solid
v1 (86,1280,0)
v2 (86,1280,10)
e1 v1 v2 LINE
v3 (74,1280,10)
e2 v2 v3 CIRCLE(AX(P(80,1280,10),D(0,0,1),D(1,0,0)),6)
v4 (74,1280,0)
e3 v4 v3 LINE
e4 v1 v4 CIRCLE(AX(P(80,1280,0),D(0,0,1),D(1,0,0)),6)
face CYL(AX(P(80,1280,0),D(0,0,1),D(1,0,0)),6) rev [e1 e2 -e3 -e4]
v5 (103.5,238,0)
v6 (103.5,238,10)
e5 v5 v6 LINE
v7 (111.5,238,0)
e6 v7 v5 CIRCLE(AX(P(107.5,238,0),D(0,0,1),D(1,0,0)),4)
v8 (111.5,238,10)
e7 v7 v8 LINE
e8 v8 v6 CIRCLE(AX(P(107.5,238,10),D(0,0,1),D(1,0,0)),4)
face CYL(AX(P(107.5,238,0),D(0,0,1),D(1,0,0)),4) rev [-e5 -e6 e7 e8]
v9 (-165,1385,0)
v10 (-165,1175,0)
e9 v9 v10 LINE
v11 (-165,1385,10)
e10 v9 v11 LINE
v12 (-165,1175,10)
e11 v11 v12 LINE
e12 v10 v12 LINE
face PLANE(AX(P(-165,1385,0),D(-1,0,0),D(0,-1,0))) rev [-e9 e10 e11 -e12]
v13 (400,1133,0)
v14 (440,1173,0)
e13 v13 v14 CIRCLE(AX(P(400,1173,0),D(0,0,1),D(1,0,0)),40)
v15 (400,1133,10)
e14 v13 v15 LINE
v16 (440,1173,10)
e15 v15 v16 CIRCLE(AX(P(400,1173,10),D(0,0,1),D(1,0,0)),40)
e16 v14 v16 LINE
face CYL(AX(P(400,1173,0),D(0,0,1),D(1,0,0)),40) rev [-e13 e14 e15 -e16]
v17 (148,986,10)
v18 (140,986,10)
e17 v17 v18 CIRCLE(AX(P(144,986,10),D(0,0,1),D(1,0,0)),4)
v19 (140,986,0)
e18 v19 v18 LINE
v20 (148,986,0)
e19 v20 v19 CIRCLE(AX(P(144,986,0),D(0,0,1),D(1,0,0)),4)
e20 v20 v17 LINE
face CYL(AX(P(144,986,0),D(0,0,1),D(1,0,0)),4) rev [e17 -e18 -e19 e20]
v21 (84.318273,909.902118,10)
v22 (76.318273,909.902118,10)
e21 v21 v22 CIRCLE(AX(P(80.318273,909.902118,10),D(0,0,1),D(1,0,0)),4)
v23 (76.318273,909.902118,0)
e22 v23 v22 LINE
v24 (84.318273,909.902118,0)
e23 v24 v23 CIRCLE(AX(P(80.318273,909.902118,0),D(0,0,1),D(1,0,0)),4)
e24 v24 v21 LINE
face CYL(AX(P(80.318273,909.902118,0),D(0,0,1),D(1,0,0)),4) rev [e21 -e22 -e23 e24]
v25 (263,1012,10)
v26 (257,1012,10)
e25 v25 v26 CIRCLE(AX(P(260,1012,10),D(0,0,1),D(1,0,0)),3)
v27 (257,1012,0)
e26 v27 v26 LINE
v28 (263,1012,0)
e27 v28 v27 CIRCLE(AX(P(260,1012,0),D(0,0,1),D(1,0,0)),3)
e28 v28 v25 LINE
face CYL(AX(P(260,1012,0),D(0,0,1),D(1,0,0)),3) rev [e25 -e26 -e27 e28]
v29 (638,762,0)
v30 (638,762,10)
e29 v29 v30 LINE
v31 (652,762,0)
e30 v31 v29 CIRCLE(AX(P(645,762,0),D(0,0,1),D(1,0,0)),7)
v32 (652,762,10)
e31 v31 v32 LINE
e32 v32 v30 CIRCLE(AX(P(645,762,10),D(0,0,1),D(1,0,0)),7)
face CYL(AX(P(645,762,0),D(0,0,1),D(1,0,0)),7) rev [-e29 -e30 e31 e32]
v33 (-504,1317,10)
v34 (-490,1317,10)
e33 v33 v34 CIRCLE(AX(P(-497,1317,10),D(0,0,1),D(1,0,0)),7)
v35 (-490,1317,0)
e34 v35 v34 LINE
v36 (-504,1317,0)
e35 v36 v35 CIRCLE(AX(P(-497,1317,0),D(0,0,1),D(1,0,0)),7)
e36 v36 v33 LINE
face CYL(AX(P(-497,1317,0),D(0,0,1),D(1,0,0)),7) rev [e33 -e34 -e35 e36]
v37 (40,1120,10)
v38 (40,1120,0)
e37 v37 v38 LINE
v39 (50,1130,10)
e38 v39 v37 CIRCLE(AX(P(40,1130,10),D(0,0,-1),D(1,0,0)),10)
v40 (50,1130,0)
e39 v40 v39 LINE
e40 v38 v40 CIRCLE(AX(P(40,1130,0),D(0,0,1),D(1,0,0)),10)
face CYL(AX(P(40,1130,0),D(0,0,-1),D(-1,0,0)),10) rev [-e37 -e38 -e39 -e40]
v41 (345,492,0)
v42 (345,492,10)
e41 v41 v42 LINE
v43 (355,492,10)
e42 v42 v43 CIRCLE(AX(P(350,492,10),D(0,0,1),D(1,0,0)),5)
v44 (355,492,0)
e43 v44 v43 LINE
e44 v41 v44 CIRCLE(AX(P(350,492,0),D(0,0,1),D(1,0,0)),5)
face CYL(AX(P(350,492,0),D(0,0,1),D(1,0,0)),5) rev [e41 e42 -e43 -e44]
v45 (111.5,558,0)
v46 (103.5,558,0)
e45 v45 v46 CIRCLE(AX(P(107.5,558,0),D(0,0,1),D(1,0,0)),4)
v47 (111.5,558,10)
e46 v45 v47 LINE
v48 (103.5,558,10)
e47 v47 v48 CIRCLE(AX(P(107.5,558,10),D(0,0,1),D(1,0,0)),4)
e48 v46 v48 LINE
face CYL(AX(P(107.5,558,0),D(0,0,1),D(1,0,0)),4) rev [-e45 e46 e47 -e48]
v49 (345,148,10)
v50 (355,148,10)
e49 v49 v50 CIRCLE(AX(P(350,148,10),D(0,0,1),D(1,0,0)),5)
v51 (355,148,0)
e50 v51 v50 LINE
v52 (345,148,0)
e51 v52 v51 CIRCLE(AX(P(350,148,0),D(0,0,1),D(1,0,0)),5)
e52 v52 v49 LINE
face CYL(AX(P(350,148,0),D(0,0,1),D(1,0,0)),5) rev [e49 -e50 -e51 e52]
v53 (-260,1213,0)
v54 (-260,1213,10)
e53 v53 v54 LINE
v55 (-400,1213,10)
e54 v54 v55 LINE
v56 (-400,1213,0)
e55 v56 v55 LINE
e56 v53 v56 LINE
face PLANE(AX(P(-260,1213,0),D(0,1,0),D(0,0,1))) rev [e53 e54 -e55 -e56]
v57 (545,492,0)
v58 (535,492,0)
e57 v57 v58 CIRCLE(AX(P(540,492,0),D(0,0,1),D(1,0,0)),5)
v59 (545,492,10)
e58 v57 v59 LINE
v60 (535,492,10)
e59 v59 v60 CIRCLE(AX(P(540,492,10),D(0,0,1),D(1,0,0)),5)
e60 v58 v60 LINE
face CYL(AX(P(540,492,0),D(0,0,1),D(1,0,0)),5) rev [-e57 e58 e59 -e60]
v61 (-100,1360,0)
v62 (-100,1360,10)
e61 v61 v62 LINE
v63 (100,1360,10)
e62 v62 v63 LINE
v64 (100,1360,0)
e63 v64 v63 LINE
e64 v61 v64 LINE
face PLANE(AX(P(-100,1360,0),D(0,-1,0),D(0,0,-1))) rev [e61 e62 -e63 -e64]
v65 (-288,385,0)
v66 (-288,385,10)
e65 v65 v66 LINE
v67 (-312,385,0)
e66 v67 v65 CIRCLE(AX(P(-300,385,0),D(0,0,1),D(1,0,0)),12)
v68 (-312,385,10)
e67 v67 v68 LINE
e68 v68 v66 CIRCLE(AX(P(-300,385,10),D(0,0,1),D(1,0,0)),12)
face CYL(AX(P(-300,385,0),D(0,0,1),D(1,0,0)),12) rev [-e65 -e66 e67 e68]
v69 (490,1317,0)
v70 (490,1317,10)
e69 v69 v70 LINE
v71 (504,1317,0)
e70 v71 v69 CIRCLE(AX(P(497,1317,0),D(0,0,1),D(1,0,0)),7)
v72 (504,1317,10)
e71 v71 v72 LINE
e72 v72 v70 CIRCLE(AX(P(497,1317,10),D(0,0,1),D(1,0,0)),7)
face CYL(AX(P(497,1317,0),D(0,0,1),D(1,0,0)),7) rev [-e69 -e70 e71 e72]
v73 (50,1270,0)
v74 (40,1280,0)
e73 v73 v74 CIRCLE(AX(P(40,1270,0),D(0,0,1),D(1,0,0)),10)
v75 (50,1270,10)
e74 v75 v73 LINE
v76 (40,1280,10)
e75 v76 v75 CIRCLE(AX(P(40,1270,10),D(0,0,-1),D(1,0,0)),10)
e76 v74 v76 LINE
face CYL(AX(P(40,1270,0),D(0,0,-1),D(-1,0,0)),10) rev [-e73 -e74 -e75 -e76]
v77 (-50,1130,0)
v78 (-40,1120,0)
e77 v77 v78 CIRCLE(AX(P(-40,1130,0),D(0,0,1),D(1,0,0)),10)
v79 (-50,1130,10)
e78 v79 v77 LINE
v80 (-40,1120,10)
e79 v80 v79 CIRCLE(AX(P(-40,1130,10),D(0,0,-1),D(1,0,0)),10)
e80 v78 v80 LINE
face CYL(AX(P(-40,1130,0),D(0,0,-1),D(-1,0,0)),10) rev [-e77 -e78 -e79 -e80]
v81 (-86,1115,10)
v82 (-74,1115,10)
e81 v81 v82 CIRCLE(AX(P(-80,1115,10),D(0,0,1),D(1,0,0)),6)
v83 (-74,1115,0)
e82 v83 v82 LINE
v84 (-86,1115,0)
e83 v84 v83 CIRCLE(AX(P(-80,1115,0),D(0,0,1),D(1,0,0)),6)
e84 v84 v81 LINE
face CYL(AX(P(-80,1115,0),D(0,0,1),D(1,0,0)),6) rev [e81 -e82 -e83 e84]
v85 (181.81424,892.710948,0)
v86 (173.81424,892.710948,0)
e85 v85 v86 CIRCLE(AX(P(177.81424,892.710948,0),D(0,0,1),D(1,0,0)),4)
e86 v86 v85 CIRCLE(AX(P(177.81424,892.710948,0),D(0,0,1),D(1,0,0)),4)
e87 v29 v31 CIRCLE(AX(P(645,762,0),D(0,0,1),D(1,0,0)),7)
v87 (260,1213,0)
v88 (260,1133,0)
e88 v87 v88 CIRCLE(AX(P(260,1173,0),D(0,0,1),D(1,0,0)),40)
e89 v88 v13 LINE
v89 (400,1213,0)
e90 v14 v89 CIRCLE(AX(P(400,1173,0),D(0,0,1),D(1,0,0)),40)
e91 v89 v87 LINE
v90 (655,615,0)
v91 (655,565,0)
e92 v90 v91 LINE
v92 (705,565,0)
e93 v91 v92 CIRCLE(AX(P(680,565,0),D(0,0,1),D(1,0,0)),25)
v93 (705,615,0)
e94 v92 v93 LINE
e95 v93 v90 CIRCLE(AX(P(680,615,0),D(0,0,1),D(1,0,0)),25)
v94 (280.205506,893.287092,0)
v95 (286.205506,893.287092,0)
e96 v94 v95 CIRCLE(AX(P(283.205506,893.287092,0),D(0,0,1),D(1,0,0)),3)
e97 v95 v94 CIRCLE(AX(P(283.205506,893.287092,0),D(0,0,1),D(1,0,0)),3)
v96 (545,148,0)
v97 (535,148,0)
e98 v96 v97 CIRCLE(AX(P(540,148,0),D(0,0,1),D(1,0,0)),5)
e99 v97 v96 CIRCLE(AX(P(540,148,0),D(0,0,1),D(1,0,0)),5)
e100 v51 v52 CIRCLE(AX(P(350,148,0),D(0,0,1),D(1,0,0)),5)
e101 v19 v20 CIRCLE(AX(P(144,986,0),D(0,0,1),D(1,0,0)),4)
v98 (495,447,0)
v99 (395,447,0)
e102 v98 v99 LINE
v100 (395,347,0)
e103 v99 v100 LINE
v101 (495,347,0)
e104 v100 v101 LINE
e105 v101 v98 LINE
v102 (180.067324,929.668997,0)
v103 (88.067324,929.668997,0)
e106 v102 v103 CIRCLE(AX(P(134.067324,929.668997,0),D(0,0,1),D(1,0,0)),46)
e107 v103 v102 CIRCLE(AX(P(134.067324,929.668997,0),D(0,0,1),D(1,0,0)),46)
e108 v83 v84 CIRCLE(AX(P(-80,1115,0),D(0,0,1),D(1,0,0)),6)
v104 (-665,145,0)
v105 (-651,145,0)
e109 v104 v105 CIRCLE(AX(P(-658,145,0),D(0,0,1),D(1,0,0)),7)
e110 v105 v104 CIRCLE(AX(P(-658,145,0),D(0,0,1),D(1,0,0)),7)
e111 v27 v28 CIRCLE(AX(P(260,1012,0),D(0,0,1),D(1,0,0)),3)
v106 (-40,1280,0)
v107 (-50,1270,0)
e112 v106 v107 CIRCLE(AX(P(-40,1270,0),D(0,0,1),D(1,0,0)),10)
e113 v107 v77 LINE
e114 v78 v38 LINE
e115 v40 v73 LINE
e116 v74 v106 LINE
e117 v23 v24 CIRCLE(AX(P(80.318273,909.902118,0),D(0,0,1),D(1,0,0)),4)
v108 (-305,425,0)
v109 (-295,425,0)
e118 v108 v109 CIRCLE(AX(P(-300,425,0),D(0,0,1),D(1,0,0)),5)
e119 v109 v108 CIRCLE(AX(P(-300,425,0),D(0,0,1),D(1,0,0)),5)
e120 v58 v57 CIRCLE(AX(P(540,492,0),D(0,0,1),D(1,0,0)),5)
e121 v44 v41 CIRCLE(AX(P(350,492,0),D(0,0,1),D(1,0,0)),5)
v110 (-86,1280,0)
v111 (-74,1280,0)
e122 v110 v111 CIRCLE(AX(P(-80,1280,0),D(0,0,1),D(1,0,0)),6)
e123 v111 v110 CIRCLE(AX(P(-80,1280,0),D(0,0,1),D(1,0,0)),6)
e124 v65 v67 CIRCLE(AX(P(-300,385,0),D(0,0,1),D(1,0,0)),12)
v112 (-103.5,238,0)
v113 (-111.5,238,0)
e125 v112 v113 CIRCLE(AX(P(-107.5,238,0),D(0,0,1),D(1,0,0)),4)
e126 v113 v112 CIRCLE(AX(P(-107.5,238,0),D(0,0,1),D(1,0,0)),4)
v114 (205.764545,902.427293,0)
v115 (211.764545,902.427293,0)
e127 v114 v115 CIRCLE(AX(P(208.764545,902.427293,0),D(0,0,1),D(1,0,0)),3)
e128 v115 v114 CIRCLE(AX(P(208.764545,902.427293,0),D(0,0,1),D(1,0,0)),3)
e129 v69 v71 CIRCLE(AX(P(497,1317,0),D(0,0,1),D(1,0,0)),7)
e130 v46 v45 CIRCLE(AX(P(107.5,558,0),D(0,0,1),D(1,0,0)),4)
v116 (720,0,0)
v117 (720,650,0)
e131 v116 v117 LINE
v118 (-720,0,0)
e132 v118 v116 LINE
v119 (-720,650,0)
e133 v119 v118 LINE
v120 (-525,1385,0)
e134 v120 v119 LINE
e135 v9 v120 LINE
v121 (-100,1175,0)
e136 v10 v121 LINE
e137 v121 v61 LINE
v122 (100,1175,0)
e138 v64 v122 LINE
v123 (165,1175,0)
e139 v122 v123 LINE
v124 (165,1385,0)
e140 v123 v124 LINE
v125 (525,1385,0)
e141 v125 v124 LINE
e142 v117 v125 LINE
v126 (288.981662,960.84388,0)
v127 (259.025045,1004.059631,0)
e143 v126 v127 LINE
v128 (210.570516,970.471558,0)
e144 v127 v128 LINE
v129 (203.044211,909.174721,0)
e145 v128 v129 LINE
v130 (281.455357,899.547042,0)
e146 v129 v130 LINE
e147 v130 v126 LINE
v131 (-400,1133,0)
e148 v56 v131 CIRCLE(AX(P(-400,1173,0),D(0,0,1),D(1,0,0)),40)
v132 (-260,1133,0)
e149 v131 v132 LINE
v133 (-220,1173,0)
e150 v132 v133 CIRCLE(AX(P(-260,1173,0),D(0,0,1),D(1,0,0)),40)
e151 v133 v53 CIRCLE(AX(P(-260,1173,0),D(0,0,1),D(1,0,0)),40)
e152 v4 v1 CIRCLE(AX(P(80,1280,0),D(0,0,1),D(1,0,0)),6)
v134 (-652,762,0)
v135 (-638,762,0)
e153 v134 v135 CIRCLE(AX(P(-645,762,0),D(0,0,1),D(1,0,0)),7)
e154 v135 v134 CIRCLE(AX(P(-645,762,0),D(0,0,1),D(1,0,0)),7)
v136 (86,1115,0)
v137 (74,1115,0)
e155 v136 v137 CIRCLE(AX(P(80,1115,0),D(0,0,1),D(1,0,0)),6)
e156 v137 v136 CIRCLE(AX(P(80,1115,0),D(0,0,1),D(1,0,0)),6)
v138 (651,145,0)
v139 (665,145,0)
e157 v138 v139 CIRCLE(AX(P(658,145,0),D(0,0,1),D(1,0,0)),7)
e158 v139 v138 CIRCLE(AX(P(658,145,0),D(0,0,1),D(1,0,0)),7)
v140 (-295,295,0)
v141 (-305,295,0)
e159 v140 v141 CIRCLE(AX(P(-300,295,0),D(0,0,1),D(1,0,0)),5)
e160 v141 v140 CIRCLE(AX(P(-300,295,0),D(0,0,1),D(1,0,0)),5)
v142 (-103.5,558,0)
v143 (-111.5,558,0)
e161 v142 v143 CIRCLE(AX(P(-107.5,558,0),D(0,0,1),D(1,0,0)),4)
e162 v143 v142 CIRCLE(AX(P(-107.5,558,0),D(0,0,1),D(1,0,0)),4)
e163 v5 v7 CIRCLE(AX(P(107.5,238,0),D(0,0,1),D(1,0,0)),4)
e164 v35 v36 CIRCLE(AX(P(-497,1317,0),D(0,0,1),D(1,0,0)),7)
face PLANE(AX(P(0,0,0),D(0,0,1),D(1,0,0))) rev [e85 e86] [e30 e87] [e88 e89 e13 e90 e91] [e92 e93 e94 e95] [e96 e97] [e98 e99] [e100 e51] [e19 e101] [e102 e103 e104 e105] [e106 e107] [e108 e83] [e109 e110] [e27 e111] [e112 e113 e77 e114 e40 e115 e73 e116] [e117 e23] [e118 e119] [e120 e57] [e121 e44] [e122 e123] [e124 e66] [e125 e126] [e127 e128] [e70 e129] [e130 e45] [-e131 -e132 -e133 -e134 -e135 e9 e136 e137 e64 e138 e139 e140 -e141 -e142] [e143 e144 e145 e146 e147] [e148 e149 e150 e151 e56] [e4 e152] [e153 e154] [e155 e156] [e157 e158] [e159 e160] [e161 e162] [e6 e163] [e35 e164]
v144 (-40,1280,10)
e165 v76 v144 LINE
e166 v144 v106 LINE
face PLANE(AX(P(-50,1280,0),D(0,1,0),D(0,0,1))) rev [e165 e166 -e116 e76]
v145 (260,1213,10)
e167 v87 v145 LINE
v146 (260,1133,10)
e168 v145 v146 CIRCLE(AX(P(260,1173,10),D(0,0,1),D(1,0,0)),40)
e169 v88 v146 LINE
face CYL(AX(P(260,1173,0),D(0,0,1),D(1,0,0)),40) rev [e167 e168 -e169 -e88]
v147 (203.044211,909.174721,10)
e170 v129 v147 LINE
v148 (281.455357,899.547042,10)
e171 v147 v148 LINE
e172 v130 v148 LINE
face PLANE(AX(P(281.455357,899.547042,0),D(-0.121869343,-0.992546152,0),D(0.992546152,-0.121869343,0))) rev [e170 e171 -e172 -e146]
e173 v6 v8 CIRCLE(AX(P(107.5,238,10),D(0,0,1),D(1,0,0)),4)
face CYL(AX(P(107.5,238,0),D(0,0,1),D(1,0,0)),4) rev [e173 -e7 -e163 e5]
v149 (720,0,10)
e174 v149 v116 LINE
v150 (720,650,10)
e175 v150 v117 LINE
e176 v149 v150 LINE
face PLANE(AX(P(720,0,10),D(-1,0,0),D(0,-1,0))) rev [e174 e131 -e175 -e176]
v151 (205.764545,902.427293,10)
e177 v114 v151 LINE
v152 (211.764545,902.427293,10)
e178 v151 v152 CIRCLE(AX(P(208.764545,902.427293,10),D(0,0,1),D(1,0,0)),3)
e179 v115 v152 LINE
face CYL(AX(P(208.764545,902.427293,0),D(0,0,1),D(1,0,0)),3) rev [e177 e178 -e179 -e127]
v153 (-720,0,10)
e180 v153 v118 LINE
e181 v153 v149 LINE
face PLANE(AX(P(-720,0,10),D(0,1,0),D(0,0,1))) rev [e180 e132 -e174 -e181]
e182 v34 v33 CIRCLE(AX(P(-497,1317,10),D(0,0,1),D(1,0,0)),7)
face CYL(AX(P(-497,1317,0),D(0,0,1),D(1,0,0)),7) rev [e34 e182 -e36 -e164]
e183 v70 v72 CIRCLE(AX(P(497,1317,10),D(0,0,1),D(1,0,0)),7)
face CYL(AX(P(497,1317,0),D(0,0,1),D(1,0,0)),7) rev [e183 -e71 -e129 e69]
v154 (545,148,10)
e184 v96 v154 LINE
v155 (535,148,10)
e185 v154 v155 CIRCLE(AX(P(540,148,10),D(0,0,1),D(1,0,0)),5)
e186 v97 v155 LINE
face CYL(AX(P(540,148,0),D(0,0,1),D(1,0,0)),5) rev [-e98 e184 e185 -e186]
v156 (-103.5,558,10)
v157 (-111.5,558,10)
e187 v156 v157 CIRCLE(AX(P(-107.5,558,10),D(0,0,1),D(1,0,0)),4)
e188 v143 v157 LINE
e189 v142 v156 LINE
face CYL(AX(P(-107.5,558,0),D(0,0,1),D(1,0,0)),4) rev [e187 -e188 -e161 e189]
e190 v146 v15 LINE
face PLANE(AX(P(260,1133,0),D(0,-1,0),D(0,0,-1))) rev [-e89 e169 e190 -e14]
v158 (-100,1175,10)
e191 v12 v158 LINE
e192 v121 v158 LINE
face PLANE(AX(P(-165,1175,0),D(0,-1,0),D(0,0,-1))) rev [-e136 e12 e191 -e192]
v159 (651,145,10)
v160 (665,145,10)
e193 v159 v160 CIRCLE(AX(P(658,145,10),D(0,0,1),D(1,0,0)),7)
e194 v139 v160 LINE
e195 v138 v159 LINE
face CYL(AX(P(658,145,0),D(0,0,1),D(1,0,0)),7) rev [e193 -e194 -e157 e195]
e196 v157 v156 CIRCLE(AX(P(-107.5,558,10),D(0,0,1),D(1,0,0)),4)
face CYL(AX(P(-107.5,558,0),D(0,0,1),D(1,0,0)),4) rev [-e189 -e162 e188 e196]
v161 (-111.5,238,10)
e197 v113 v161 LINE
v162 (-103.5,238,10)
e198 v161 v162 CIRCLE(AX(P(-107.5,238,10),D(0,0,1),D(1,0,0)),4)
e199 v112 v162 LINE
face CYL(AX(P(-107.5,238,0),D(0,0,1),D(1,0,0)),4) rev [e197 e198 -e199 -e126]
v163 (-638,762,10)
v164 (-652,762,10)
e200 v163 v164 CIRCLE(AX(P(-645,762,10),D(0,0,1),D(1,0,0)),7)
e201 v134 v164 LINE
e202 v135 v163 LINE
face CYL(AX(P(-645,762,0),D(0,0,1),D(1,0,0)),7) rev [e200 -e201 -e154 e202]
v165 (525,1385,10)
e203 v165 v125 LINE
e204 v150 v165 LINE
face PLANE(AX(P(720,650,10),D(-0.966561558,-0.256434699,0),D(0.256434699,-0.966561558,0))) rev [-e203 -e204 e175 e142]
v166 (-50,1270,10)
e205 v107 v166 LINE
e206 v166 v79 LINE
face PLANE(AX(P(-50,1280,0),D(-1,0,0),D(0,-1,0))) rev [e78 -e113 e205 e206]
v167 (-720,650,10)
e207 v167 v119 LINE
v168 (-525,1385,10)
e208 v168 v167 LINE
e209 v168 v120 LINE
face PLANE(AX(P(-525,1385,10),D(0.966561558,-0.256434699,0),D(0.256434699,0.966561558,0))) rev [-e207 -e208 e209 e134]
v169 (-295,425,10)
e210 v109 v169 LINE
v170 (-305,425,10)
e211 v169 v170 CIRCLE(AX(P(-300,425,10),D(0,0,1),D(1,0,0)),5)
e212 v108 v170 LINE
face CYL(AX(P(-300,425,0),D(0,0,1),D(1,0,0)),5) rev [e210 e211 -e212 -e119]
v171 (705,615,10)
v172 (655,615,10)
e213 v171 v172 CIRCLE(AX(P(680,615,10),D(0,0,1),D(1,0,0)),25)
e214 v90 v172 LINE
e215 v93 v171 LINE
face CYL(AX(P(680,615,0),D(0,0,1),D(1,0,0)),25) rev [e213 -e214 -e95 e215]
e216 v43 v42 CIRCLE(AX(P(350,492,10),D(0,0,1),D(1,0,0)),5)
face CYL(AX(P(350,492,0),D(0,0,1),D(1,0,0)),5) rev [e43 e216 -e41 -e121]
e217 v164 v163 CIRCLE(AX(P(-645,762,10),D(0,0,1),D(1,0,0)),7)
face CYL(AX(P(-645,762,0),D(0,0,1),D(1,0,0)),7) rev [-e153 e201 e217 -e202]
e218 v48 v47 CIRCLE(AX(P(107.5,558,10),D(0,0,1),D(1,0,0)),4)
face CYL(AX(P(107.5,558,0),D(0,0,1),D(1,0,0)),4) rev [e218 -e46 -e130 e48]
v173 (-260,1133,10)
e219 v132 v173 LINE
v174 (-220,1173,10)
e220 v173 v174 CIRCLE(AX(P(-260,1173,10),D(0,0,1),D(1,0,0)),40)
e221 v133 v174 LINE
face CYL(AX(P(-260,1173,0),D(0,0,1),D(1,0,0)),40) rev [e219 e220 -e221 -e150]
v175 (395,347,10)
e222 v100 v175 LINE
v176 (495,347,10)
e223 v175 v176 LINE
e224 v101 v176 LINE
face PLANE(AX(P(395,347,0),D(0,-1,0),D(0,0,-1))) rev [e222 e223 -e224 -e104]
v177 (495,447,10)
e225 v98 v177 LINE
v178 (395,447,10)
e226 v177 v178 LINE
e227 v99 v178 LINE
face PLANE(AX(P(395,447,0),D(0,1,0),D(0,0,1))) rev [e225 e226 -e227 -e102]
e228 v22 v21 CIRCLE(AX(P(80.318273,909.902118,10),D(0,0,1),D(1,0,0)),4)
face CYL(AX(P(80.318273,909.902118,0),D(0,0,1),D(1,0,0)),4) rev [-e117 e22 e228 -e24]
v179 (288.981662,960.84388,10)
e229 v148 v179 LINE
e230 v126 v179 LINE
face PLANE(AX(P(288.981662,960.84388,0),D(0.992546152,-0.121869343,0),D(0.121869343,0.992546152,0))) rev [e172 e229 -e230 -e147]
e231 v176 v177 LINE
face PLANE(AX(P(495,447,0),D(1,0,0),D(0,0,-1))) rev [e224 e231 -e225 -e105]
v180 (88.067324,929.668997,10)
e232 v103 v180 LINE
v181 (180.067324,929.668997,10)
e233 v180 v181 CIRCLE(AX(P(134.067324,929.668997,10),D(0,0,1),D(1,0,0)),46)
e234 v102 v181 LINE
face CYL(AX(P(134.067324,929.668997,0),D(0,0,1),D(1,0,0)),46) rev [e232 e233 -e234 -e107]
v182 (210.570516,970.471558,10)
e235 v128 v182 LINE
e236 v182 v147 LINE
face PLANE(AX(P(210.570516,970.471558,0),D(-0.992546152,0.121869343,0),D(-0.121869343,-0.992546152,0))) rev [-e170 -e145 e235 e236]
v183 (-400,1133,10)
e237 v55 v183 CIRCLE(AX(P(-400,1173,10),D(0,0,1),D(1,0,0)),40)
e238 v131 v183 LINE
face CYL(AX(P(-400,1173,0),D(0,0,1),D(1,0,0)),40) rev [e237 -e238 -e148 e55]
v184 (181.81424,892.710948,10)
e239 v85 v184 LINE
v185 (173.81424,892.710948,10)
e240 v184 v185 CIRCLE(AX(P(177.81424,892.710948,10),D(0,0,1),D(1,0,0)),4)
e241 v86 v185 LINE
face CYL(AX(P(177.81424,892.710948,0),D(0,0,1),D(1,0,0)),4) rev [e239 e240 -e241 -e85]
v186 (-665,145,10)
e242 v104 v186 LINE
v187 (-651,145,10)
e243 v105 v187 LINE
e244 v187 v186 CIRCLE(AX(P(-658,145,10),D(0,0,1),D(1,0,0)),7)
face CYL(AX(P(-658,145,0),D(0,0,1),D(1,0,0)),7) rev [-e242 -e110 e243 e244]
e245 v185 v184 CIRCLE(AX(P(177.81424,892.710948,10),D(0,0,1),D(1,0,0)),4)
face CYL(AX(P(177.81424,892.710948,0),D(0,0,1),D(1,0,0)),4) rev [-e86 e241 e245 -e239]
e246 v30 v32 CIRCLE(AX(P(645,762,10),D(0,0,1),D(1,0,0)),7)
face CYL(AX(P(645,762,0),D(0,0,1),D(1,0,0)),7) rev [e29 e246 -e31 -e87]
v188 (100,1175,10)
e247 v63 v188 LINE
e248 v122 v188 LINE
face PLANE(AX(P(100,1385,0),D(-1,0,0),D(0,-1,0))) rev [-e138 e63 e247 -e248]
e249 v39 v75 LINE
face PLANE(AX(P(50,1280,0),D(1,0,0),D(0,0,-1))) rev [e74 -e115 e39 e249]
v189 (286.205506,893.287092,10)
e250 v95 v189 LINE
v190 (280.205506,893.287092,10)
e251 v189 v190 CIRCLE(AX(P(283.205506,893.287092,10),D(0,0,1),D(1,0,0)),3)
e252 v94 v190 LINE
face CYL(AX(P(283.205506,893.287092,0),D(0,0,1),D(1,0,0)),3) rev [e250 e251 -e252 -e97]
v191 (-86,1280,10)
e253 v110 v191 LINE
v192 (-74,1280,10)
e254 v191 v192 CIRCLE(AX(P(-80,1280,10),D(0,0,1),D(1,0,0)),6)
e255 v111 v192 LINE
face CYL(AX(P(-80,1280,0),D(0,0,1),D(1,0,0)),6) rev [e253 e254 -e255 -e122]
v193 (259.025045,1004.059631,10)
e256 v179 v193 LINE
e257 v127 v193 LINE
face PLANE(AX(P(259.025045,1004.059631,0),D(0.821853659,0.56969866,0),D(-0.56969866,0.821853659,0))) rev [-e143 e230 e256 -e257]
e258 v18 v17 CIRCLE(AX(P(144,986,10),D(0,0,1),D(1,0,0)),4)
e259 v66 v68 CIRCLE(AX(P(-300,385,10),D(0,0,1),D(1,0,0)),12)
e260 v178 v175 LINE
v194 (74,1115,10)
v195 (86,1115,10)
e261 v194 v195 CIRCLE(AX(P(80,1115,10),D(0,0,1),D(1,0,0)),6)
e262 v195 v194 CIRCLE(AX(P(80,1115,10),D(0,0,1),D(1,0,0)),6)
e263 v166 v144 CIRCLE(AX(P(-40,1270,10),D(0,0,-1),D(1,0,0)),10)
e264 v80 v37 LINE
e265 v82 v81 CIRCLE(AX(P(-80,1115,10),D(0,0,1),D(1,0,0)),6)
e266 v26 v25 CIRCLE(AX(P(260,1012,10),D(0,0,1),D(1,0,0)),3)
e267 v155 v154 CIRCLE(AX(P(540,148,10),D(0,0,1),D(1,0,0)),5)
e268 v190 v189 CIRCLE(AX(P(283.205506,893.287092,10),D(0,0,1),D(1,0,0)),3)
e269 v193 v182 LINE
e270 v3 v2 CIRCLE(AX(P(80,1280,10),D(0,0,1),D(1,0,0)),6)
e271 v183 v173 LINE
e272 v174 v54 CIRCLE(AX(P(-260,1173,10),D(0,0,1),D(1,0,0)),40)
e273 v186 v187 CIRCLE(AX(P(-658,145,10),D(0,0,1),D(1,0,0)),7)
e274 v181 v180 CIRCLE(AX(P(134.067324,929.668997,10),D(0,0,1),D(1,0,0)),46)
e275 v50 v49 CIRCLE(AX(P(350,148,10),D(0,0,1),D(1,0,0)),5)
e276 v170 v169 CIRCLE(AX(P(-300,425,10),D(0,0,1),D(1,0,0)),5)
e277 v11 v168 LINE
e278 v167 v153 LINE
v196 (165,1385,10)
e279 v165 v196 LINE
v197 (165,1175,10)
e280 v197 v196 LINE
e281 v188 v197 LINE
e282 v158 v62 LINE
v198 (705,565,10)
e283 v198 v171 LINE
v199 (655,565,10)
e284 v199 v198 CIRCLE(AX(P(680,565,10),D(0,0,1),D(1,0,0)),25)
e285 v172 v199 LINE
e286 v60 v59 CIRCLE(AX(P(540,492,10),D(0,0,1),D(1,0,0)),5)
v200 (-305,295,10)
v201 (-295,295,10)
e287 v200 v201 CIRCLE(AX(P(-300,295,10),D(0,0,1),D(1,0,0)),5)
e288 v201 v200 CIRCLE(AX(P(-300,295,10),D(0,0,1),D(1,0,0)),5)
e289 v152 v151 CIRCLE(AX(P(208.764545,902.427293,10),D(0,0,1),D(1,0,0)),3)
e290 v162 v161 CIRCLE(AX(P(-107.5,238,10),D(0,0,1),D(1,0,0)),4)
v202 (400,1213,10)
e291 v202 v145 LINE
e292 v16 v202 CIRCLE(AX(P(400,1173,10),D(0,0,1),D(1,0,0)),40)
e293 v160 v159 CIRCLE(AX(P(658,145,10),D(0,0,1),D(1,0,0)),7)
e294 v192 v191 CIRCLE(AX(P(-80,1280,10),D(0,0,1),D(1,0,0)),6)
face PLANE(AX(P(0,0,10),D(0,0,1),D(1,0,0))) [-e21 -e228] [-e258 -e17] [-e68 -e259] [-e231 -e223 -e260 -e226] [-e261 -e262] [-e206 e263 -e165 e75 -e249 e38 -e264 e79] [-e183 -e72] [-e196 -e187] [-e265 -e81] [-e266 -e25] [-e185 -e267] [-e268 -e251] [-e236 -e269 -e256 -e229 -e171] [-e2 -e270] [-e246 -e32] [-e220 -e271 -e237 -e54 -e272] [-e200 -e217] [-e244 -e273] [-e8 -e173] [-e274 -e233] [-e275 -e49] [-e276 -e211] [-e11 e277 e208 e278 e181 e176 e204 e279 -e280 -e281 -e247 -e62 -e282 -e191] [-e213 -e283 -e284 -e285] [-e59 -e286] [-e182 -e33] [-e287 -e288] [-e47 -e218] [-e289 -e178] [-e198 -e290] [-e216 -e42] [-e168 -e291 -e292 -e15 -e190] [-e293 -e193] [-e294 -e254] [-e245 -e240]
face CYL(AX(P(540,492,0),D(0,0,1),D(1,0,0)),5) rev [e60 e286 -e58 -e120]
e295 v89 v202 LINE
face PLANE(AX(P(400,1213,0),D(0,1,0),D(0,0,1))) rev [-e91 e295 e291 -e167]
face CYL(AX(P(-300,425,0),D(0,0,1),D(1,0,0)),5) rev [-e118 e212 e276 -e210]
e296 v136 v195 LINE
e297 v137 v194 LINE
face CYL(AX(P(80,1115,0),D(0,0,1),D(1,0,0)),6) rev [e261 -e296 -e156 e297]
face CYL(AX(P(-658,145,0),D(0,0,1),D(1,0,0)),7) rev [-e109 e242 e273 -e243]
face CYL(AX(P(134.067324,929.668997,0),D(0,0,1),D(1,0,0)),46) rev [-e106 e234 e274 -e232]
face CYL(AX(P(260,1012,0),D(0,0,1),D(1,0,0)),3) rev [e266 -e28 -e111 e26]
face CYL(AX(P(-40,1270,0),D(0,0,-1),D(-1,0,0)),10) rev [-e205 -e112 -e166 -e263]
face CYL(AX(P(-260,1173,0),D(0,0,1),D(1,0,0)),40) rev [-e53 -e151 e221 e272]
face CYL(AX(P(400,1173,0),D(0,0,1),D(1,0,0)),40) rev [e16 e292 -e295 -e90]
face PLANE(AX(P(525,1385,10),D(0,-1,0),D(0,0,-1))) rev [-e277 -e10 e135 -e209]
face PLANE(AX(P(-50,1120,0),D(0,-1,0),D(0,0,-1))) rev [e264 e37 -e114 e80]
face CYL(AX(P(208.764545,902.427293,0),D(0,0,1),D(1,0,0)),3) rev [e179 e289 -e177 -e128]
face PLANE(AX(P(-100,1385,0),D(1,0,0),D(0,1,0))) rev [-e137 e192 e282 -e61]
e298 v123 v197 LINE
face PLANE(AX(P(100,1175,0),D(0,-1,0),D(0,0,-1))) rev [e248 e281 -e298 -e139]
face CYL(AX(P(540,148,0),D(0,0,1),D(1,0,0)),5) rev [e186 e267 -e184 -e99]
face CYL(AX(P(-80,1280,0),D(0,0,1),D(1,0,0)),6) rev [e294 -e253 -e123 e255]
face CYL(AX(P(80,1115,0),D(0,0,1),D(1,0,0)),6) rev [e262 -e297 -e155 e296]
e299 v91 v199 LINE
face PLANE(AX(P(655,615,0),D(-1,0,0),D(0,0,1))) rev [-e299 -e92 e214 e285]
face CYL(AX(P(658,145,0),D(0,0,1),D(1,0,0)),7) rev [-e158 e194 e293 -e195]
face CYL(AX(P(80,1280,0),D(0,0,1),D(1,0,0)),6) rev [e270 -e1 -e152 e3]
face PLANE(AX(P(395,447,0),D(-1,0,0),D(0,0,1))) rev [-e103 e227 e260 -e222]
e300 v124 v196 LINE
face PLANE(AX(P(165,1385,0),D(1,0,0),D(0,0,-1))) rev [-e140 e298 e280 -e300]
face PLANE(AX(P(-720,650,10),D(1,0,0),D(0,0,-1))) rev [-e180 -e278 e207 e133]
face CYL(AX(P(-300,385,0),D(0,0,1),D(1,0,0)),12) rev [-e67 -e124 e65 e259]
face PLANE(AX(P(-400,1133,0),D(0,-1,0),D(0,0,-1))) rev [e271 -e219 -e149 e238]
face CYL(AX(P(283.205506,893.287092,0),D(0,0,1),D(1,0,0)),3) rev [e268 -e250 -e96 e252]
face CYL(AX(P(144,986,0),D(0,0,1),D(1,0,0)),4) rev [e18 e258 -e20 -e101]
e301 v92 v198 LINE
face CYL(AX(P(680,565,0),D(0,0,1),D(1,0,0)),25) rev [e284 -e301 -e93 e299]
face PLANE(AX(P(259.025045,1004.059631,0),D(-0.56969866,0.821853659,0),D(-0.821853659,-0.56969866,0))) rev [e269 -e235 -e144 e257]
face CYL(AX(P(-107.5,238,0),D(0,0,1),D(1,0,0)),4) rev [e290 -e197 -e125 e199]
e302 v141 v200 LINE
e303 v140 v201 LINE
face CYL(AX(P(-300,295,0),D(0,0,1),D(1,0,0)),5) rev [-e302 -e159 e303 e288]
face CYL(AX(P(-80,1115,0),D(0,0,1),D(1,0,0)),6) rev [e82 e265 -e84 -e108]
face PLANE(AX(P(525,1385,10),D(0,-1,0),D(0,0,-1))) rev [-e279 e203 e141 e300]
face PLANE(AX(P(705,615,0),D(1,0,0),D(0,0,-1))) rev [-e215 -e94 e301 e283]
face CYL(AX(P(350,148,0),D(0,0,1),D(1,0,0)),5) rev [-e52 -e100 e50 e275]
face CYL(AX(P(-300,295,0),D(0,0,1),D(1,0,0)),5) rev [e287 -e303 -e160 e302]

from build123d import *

# Parameters (mm, degrees)
BOSS_EXTRUDE1_DEPTH  = 10
SKETCH2_R            = 7
CUT_EXTRUDE1_DEPTH   = 10
LPATTERN1_COUNT      = 2
LPATTERN1_PITCH      = 1316
SKETCH3_R            = 7
CUT_EXTRUDE2_DEPTH   = 10
LPATTERN2_COUNT      = 2
LPATTERN2_PITCH      = 1290
SKETCH4_R            = 7
CUT_EXTRUDE3_DEPTH   = 10
LPATTERN3_COUNT      = 2
LPATTERN3_PITCH      = 994
CUT_EXTRUDE4_DEPTH   = 10
SKETCH6_W            = 100
SKETCH6_H            = 100
CUT_EXTRUDE5_DEPTH   = 10
SKETCH7_R            = 5
CUT_EXTRUDE6_DEPTH   = 10
LPATTERN4_COUNT      = 2
LPATTERN4_PITCH      = 190
LPATTERN4_COUNT_DIR2 = 2
LPATTERN4_PITCH_DIR2 = 344
SKETCH8_R            = 4
CUT_EXTRUDE7_DEPTH   = 10
LPATTERN5_COUNT      = 2
LPATTERN5_PITCH      = 320
LPATTERN5_COUNT_DIR2 = 2
LPATTERN5_PITCH_DIR2 = 215
CUT_EXTRUDE8_DEPTH   = 10
LPATTERN6_COUNT      = 2
LPATTERN6_PITCH      = 660
SKETCH10_W           = 100
SKETCH10_H           = 160
CUT_EXTRUDE9_DEPTH   = 10
FILLET1_R            = 10
SKETCH11_R           = 6
CUT_EXTRUDE10_DEPTH  = 10
LPATTERN7_COUNT      = 2
LPATTERN7_PITCH      = 160
LPATTERN7_COUNT_DIR2 = 2
LPATTERN7_PITCH_DIR2 = 165
SKETCH12_R           = 4
CUT_EXTRUDE11_DEPTH  = 10
SKETCH14_R           = 46
CUT_EXTRUDE12_DEPTH  = 10
SKETCH15_R           = 4
CUT_EXTRUDE13_DEPTH  = 10
LPATTERN8_COUNT      = 2
LPATTERN8_PITCH      = 99
SKETCH16_R           = 3
CUT_EXTRUDE14_DEPTH  = 10
CUT_EXTRUDE15_DEPTH  = 10
SKETCH18_R           = 3
CUT_EXTRUDE16_DEPTH  = 10
LPATTERN9_COUNT      = 2
LPATTERN9_PITCH      = 75
SKETCH19_R           = 5
CUT_EXTRUDE17_DEPTH  = 10
LPATTERN10_COUNT     = 2
LPATTERN10_PITCH     = 130
SKETCH20_R           = 12
CUT_EXTRUDE18_DEPTH  = 10
SKETCH21_W           = 65
SKETCH21_H           = 210
CUT_EXTRUDE19_DEPTH  = 10
SKETCH22_W           = 65
SKETCH22_H           = 210
CUT_EXTRUDE20_DEPTH  = 10
SKETCH23_W           = 200
SKETCH23_H           = 25
CUT_EXTRUDE21_DEPTH  = 10


with BuildPart() as part:
    # Sketch1 → Boss-Extrude1 (new body)
    with BuildSketch(Plane.XY):
        Polygon((-720, 0), (720, 0), (720, 650), (525, 1385), (-525, 1385), (-720, 650), align=None)
    extrude(amount=BOSS_EXTRUDE1_DEPTH)

    # Sketch2 → Cut-Extrude1 (cut)
    with BuildSketch(Plane.XY.offset(10)):
        with Locations((-658, 145)):
            Circle(SKETCH2_R)
    cut_extrude1 = extrude(amount=-CUT_EXTRUDE1_DEPTH, mode=Mode.SUBTRACT)

    # LPattern1: Cut-Extrude1 ×2
    with Locations(*[(i * LPATTERN1_PITCH, 0, 0) for i in range(1, LPATTERN1_COUNT)]):
        add(cut_extrude1, mode=Mode.SUBTRACT)

    # Sketch3 → Cut-Extrude2 (cut)
    with BuildSketch(Plane.XY.offset(10)):
        with Locations((-645, 762)):
            Circle(SKETCH3_R)
    cut_extrude2 = extrude(amount=-CUT_EXTRUDE2_DEPTH, mode=Mode.SUBTRACT)

    # LPattern2: Cut-Extrude2 ×2
    with Locations(*[(i * LPATTERN2_PITCH, 0, 0) for i in range(1, LPATTERN2_COUNT)]):
        add(cut_extrude2, mode=Mode.SUBTRACT)

    # Sketch4 → Cut-Extrude3 (cut)
    with BuildSketch(Plane.XY.offset(10)):
        with Locations((-497, 1317)):
            Circle(SKETCH4_R)
    cut_extrude3 = extrude(amount=-CUT_EXTRUDE3_DEPTH, mode=Mode.SUBTRACT)

    # LPattern3: Cut-Extrude3 ×2
    with Locations(*[(i * LPATTERN3_PITCH, 0, 0) for i in range(1, LPATTERN3_COUNT)]):
        add(cut_extrude3, mode=Mode.SUBTRACT)

    # Sketch5 → Cut-Extrude4 (cut)
    with BuildSketch(Plane.XY.offset(10)):
        with BuildLine():
            Line((655, 615), (655, 565))
            ThreePointArc((655, 565), (680, 540), (705, 565))
            Line((705, 565), (705, 615))
            ThreePointArc((705, 615), (680, 640), (655, 615))
        make_face()
    extrude(amount=-CUT_EXTRUDE4_DEPTH, mode=Mode.SUBTRACT)

    # Sketch6 → Cut-Extrude5 (cut)
    with BuildSketch(Plane.XY.offset(10)):
        with Locations((445, 397)):
            Rectangle(SKETCH6_W, SKETCH6_H)
    extrude(amount=-CUT_EXTRUDE5_DEPTH, mode=Mode.SUBTRACT)

    # Sketch7 → Cut-Extrude6 (cut)
    with BuildSketch(Plane.XY.offset(10)):
        with Locations((540, 492)):
            Circle(SKETCH7_R)
    cut_extrude6 = extrude(amount=-CUT_EXTRUDE6_DEPTH, mode=Mode.SUBTRACT)

    # LPattern4: Cut-Extrude6 2 × 2
    with Locations(*[(-i * LPATTERN4_PITCH, -j * LPATTERN4_PITCH_DIR2, 0) for i in range(LPATTERN4_COUNT) for j in range(LPATTERN4_COUNT_DIR2) if (i, j) != (0, 0)]):
        add(cut_extrude6, mode=Mode.SUBTRACT)

    # Sketch8 → Cut-Extrude7 (cut)
    with BuildSketch(Plane.XY.offset(10)):
        with Locations((107.5, 238)):
            Circle(SKETCH8_R)
    cut_extrude7 = extrude(amount=-CUT_EXTRUDE7_DEPTH, mode=Mode.SUBTRACT)

    # LPattern5: Cut-Extrude7 2 × 2
    with Locations(*[(-j * LPATTERN5_PITCH_DIR2, i * LPATTERN5_PITCH, 0) for i in range(LPATTERN5_COUNT) for j in range(LPATTERN5_COUNT_DIR2) if (i, j) != (0, 0)]):
        add(cut_extrude7, mode=Mode.SUBTRACT)

    # Sketch9 → Cut-Extrude8 (cut)
    with BuildSketch(Plane.XY.offset(10)):
        with BuildLine():
            Line((-400, 1133), (-260, 1133))
            ThreePointArc((-260, 1133), (-220, 1173), (-260, 1213))
            Line((-260, 1213), (-400, 1213))
            ThreePointArc((-400, 1213), (-440, 1173), (-400, 1133))
        make_face()
    cut_extrude8 = extrude(amount=-CUT_EXTRUDE8_DEPTH, mode=Mode.SUBTRACT)

    # LPattern6: Cut-Extrude8 ×2
    with Locations(*[(i * LPATTERN6_PITCH, 0, 0) for i in range(1, LPATTERN6_COUNT)]):
        add(cut_extrude8, mode=Mode.SUBTRACT)

    # Sketch10 → Cut-Extrude9 (cut)
    with BuildSketch(Plane.XY.offset(10)):
        with Locations((0, 1200)):
            Rectangle(SKETCH10_W, SKETCH10_H)
    extrude(amount=-CUT_EXTRUDE9_DEPTH, mode=Mode.SUBTRACT)

    # Fillet1
    fillet1_edges = [part.edges().sort_by_distance(p)[0] for p in [
        (-50, 1120, 5),
        (-50, 1280, 5),
        (50, 1280, 5),
        (50, 1120, 5),
    ]]
    fillet(fillet1_edges, radius=FILLET1_R)

    # Sketch11 → Cut-Extrude10 (cut)
    with BuildSketch(Plane.XY.offset(10)):
        with Locations((80, 1280)):
            Circle(SKETCH11_R)
    cut_extrude10 = extrude(amount=-CUT_EXTRUDE10_DEPTH, mode=Mode.SUBTRACT)

    # LPattern7: Cut-Extrude10 2 × 2
    with Locations(*[(-i * LPATTERN7_PITCH, -j * LPATTERN7_PITCH_DIR2, 0) for i in range(LPATTERN7_COUNT) for j in range(LPATTERN7_COUNT_DIR2) if (i, j) != (0, 0)]):
        add(cut_extrude10, mode=Mode.SUBTRACT)

    # Sketch12 → Cut-Extrude11 (cut)
    with BuildSketch(Plane.XY.offset(10)):
        with Locations((144, 986)):
            Circle(SKETCH12_R)
    extrude(amount=-CUT_EXTRUDE11_DEPTH, mode=Mode.SUBTRACT)

    # Sketch14 → Cut-Extrude12 (cut)
    with BuildSketch(Plane.XY.offset(10)):
        with Locations((134.067324237, 929.668996528)):
            Circle(SKETCH14_R)
    extrude(amount=-CUT_EXTRUDE12_DEPTH, mode=Mode.SUBTRACT)

    # Sketch15 → Cut-Extrude13 (cut)
    with BuildSketch(Plane.XY.offset(10)):
        with Locations((80.318272947, 909.902118035)):
            Circle(SKETCH15_R)
    cut_extrude13 = extrude(amount=-CUT_EXTRUDE13_DEPTH, mode=Mode.SUBTRACT)

    # LPattern8: Cut-Extrude13 ×2
    with Locations(*[Vector(0.9848077530122089, -0.17364817766692592, 0) * (i * LPATTERN8_PITCH) for i in range(1, LPATTERN8_COUNT)]):
        add(cut_extrude13, mode=Mode.SUBTRACT)

    # Sketch16 → Cut-Extrude14 (cut)
    with BuildSketch(Plane.XY.offset(10)):
        with Locations((260, 1012)):
            Circle(SKETCH16_R)
    extrude(amount=-CUT_EXTRUDE14_DEPTH, mode=Mode.SUBTRACT)

    # Sketch17 → Cut-Extrude15 (cut)
    with BuildSketch(Plane.XY.offset(10)):
        Polygon((259.025045253, 1004.059630787), (210.570516199, 970.471558288), (203.044210897, 909.174720581), (281.455356876, 899.547042452), (288.981662179, 960.843880159), align=None)
    extrude(amount=-CUT_EXTRUDE15_DEPTH, mode=Mode.SUBTRACT)

    # Sketch18 → Cut-Extrude16 (cut)
    with BuildSketch(Plane.XY.offset(10)):
        with Locations((208.764544822, 902.427292939)):
            Circle(SKETCH18_R)
    cut_extrude16 = extrude(amount=-CUT_EXTRUDE16_DEPTH, mode=Mode.SUBTRACT)

    # LPattern9: Cut-Extrude16 ×2
    with Locations(*[Vector(0.9925461516413229, -0.121869343405141, 0) * (i * LPATTERN9_PITCH) for i in range(1, LPATTERN9_COUNT)]):
        add(cut_extrude16, mode=Mode.SUBTRACT)

    # Sketch19 → Cut-Extrude17 (cut)
    with BuildSketch(Plane.XY.offset(10)):
        with Locations((-300, 295)):
            Circle(SKETCH19_R)
    cut_extrude17 = extrude(amount=-CUT_EXTRUDE17_DEPTH, mode=Mode.SUBTRACT)

    # LPattern10: Cut-Extrude17 ×2
    with Locations(*[(0, i * LPATTERN10_PITCH, 0) for i in range(1, LPATTERN10_COUNT)]):
        add(cut_extrude17, mode=Mode.SUBTRACT)

    # Sketch20 → Cut-Extrude18 (cut)
    with BuildSketch(Plane.XY.offset(10)):
        with Locations((-300, 385)):
            Circle(SKETCH20_R)
    extrude(amount=-CUT_EXTRUDE18_DEPTH, mode=Mode.SUBTRACT)

    # Sketch21 → Cut-Extrude19 (cut)
    with BuildSketch(Plane.XY.offset(10)):
        with Locations((132.5, 1280)):
            Rectangle(SKETCH21_W, SKETCH21_H)
    extrude(amount=-CUT_EXTRUDE19_DEPTH, mode=Mode.SUBTRACT)

    # Sketch22 → Cut-Extrude20 (cut)
    with BuildSketch(Plane.XY.offset(10)):
        with Locations((-132.5, 1280)):
            Rectangle(SKETCH22_W, SKETCH22_H)
    extrude(amount=-CUT_EXTRUDE20_DEPTH, mode=Mode.SUBTRACT)

    # Sketch23 → Cut-Extrude21 (cut)
    with BuildSketch(Plane.XY.offset(10)):
        with Locations((0, 1372.5)):
            Rectangle(SKETCH23_W, SKETCH23_H)
    extrude(amount=-CUT_EXTRUDE21_DEPTH, mode=Mode.SUBTRACT)


solid = part.part
